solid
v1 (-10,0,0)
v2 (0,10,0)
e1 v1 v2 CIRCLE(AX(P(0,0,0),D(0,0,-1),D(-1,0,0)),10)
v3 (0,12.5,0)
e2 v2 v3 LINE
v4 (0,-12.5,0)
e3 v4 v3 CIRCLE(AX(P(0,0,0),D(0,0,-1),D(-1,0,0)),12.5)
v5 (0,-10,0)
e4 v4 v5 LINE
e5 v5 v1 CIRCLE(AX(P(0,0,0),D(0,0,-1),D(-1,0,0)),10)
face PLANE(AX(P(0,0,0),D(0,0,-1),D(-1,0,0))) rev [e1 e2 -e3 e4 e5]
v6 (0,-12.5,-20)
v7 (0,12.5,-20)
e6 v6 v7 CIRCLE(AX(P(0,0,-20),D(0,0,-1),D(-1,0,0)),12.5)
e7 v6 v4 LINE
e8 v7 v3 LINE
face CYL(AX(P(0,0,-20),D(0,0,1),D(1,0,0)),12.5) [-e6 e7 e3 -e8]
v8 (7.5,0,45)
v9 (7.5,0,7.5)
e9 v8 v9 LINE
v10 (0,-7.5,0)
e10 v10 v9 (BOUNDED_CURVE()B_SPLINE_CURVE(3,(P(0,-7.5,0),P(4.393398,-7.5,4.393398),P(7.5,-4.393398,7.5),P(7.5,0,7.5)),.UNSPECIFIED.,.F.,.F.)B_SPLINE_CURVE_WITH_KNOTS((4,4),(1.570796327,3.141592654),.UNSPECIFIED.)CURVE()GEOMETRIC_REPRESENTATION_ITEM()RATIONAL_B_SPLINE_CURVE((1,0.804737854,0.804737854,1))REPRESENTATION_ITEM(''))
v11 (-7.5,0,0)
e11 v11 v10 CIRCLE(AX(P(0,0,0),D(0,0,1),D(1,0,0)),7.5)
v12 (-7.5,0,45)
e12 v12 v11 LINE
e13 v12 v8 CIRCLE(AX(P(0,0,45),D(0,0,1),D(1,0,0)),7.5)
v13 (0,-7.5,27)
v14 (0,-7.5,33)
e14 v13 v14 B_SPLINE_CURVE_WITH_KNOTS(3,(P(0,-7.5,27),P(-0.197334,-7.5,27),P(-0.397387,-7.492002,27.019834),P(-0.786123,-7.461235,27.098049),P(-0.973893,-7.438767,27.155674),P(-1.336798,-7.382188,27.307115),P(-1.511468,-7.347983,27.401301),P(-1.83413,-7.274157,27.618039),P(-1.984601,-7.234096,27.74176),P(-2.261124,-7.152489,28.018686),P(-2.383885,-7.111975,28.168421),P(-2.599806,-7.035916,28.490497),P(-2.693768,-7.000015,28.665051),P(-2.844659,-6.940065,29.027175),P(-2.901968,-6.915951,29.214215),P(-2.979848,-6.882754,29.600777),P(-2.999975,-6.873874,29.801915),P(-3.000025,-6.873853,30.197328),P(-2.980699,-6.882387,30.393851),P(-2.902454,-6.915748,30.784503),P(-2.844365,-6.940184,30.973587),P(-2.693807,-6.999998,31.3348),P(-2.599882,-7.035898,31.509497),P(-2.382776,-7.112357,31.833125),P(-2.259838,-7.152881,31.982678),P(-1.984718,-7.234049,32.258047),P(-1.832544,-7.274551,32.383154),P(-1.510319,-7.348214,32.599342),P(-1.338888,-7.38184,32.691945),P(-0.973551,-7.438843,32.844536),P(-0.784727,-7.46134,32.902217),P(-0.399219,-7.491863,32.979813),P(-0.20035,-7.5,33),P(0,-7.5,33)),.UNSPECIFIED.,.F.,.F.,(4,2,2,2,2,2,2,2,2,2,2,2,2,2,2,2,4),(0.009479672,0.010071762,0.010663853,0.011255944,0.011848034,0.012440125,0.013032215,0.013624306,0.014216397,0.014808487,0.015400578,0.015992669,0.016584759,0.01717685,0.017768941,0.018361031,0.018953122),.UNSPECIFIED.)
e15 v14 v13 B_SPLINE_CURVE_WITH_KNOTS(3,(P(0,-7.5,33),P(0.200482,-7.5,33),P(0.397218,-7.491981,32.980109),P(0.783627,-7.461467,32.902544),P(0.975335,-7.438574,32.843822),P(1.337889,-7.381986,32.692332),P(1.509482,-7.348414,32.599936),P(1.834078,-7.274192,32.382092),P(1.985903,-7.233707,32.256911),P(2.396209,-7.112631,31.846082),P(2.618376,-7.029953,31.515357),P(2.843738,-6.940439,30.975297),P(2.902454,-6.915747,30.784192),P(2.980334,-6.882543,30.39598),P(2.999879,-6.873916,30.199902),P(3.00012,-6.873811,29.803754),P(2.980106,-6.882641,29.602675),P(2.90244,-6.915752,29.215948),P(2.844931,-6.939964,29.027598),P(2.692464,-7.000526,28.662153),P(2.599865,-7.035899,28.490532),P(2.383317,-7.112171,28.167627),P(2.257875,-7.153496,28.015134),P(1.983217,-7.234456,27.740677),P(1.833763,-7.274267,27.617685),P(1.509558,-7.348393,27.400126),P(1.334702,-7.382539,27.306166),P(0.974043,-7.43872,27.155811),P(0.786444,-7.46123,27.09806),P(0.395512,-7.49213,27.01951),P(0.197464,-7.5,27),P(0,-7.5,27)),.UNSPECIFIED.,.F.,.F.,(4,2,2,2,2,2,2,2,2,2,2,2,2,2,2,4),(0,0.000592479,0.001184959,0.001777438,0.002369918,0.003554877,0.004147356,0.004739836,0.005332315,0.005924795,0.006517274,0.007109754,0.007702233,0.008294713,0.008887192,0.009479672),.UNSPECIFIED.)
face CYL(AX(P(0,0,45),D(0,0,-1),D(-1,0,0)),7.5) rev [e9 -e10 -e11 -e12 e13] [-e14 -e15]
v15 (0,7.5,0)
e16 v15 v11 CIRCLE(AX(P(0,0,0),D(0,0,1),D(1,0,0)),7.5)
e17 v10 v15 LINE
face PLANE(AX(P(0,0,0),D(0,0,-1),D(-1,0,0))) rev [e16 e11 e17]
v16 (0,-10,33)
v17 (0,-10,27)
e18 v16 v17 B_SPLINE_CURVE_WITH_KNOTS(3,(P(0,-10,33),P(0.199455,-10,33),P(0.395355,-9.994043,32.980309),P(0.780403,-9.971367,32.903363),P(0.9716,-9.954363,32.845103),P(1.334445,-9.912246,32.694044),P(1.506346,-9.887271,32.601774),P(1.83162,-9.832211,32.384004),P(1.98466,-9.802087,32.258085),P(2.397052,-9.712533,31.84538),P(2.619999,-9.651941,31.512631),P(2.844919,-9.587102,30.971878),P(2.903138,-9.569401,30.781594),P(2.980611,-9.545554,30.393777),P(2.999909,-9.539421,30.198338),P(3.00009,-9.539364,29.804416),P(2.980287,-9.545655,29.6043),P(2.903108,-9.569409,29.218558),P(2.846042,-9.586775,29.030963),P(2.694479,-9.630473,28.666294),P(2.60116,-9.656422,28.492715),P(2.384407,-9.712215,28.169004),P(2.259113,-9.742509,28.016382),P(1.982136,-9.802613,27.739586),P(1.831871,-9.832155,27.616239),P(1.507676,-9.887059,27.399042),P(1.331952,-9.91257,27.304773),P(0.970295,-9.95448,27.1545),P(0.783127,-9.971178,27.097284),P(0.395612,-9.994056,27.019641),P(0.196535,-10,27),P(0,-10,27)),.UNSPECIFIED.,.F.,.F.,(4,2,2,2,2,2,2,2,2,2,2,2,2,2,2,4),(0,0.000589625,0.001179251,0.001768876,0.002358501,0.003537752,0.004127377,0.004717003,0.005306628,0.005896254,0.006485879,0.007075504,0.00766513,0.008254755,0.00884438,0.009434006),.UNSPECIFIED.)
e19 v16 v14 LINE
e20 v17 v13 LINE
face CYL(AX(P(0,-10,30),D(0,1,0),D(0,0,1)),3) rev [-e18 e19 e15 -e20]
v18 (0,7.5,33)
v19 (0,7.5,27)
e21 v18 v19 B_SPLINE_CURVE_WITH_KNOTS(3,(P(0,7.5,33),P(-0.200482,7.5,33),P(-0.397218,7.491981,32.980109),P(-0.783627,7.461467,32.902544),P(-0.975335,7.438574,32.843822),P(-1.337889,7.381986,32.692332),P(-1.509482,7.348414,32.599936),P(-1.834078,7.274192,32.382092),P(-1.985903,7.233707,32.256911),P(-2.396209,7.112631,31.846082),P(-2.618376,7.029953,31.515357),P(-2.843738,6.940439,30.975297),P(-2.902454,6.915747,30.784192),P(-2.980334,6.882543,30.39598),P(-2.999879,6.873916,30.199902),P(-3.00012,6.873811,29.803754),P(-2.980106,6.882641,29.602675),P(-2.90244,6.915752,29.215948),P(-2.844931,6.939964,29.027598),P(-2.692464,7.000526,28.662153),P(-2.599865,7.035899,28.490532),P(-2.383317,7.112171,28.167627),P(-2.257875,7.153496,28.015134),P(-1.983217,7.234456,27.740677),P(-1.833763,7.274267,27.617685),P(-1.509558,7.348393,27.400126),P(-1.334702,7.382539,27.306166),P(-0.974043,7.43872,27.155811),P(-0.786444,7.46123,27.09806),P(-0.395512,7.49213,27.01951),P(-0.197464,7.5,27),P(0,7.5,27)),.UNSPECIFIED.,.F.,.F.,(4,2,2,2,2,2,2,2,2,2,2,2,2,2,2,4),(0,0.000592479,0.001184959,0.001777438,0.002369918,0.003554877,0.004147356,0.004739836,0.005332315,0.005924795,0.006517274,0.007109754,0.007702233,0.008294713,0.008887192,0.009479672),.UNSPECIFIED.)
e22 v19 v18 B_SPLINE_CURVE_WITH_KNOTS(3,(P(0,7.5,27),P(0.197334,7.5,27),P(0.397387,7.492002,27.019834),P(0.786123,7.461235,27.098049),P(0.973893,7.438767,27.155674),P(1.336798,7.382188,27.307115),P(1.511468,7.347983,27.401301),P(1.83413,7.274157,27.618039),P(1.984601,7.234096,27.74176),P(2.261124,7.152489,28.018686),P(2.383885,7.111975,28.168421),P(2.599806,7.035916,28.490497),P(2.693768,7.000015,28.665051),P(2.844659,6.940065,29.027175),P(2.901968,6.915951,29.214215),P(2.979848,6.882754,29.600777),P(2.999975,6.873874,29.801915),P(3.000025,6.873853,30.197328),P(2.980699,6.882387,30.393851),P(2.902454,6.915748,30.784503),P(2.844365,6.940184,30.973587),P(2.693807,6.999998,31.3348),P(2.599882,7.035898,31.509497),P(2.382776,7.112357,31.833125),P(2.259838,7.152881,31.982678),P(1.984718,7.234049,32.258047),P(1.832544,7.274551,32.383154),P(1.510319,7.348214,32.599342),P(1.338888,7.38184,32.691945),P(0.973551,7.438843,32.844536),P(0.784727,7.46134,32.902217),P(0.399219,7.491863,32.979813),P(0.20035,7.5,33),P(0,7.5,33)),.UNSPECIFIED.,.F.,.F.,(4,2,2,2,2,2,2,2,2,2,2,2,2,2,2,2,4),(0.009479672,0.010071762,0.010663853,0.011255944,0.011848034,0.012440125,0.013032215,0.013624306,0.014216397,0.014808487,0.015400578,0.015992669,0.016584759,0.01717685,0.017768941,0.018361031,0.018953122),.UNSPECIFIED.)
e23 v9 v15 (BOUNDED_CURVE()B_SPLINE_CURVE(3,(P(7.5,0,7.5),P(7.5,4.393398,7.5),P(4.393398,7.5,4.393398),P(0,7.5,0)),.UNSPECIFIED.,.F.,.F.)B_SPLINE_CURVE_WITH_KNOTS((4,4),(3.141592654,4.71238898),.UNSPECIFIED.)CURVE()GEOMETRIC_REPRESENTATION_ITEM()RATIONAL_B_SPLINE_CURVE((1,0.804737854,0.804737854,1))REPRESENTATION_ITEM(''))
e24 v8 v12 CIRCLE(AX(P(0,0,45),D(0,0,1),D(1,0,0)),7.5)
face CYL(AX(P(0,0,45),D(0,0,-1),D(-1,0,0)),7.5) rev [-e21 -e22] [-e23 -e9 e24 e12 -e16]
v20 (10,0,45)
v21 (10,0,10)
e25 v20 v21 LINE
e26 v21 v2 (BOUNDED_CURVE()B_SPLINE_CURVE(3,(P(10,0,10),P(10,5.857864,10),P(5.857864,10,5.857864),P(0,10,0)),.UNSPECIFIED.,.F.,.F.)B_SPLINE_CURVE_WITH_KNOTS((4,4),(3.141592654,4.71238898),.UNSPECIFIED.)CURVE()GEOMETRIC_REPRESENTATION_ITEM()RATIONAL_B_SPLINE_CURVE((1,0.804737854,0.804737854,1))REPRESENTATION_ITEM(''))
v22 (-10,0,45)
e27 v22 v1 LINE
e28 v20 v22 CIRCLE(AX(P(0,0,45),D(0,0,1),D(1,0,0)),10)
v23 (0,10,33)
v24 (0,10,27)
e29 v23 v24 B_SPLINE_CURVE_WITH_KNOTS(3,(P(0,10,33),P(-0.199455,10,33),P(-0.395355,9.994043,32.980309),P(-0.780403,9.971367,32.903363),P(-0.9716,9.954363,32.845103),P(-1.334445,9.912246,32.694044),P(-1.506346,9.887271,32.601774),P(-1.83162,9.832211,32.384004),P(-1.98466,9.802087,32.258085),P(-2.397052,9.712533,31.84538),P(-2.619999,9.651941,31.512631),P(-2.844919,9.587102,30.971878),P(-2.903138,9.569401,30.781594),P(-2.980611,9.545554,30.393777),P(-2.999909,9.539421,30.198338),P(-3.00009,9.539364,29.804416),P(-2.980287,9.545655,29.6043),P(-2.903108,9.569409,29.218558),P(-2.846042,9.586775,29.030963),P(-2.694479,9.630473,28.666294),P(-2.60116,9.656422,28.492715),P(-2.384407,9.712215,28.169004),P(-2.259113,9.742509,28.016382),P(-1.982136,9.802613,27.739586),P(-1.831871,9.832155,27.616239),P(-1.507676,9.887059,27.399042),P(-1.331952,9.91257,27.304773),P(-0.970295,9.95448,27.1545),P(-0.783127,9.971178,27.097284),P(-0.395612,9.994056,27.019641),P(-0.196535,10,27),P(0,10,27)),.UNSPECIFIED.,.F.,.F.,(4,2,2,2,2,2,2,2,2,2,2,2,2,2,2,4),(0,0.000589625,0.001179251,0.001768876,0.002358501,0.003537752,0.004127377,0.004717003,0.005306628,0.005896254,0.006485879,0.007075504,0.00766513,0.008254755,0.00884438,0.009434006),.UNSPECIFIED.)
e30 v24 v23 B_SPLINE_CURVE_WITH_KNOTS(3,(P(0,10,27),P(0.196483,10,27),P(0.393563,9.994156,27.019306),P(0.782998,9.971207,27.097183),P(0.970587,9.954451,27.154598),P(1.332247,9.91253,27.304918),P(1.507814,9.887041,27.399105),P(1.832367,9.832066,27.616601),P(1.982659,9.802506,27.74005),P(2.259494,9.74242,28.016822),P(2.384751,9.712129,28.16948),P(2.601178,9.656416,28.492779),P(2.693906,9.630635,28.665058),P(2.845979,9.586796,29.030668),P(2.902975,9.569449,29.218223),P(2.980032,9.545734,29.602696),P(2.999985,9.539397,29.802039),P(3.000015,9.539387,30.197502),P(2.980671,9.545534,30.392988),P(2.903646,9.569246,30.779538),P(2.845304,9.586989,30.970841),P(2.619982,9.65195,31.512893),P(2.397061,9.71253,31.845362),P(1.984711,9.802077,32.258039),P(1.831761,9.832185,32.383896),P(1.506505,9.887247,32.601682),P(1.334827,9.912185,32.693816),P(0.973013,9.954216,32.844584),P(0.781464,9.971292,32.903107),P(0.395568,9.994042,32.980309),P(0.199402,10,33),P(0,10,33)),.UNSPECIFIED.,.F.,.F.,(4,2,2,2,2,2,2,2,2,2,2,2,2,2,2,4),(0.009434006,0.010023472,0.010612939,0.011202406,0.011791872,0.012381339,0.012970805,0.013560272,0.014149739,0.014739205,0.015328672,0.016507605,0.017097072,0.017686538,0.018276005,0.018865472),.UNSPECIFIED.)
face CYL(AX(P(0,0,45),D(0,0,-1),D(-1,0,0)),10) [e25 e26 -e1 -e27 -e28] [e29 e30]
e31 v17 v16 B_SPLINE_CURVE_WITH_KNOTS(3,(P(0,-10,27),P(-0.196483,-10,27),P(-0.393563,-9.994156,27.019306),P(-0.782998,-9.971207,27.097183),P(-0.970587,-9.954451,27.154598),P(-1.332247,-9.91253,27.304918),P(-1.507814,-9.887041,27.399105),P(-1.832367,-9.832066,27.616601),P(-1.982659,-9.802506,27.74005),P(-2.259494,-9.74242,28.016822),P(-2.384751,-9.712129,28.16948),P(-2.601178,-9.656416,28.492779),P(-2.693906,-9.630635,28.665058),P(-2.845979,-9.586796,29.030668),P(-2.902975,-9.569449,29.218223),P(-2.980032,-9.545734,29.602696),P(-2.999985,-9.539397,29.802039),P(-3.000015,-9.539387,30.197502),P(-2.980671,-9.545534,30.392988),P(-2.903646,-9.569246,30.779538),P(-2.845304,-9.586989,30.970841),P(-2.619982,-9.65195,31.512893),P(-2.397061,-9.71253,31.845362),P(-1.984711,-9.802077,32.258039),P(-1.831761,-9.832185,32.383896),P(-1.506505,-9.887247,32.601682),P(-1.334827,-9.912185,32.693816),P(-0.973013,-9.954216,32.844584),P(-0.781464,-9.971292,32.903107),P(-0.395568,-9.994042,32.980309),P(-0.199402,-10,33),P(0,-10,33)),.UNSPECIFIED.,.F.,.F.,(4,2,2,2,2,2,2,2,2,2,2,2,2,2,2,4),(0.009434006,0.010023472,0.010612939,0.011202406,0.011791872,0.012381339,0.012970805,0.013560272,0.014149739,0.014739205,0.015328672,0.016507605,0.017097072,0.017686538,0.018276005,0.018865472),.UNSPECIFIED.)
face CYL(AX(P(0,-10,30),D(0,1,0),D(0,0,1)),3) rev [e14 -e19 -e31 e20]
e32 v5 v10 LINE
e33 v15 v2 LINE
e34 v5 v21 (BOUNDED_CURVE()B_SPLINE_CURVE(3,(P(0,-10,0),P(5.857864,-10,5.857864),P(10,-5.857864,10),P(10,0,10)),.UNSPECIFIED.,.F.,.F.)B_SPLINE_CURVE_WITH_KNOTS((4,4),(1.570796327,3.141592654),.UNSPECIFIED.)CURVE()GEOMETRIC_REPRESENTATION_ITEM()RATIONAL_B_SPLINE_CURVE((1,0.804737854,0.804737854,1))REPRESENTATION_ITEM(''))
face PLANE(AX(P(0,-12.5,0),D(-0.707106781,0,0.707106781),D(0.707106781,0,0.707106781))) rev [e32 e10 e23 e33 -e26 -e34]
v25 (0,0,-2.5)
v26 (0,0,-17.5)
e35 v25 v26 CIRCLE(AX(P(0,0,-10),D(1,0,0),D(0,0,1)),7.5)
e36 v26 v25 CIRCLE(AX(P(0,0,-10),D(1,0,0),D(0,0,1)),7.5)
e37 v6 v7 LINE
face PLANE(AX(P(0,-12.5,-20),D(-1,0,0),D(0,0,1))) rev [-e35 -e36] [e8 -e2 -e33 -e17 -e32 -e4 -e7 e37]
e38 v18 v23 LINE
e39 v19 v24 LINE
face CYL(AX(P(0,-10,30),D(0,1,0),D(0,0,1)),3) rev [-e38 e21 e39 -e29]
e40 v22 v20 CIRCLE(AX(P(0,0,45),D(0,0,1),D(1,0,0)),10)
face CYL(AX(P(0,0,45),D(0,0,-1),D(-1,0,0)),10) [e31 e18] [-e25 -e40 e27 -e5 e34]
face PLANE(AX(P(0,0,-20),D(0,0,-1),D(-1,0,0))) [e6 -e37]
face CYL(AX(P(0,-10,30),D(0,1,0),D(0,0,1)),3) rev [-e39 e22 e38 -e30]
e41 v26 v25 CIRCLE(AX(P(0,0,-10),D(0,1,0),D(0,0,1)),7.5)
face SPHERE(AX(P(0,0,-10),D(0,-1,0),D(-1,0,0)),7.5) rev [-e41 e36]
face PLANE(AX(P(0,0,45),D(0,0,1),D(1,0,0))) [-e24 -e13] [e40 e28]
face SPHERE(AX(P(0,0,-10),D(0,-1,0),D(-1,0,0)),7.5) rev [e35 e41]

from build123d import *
from build123d.topology import SkipClean

# Parameters (mm, degrees)
SKETCH1_R               = 10
SKETCH1_R_2             = 7.5
BOSS_EXTRUDE1_DEPTH     = 45
CUT_EXTRUDE1_DEPTH      = 48.16990566
CUT_EXTRUDE1_DEPTH_BACK = 48.16990566
SKETCH2_R               = 3
SKETCH3_R               = 12.5
BOSS_EXTRUDE2_DEPTH     = 20
CUT_EXTRUDE2_DEPTH      = 49.347699108
CUT_EXTRUDE2_DEPTH_BACK = 49.347699108


with BuildPart() as part:
    # Sketch1 → Boss-Extrude1 (new body)
    with BuildSketch(Plane.XY):
        with Locations(Location((0, 0, 0), (0, 0, 180))):
            Circle(SKETCH1_R)
        with Locations(Location((0, 0, 0), (0, 0, 180))):
            Circle(SKETCH1_R_2, mode=Mode.SUBTRACT)
    extrude(amount=BOSS_EXTRUDE1_DEPTH)

    # Sketch2 → Cut-Extrude1 (cut, two sides: drawn at the far end of the back side and taken through both)
    with BuildSketch(Plane(origin=(0, 0, 0), x_dir=(1, 0, 0), z_dir=(0, 1, 0)).offset(-CUT_EXTRUDE1_DEPTH_BACK)):
        with Locations(Location((0, -30, 0), (0, 0, 270))):
            Circle(SKETCH2_R)
    extrude(amount=CUT_EXTRUDE1_DEPTH + CUT_EXTRUDE1_DEPTH_BACK, mode=Mode.SUBTRACT)

    # Sketch3 → Boss-Extrude2 (add)
    with BuildSketch(Plane(origin=(0, 0, 0), x_dir=(-1, 0, 0), z_dir=(0, 0, -1))):
        Circle(SKETCH3_R)
    extrude(amount=BOSS_EXTRUDE2_DEPTH)

    # Sketch4 → Cut-Extrude2 (cut, two sides: drawn at the far end of the back side and taken through both)
    with BuildSketch(Plane(origin=(0, 0, 0), x_dir=(1, 0, 0), z_dir=(0, 1, 0)).offset(-CUT_EXTRUDE2_DEPTH_BACK)):
        Polygon((0, 20), (12.5, 20), (12.5, 0), (10, -10), (0, 0), align=None)
    extrude(amount=CUT_EXTRUDE2_DEPTH + CUT_EXTRUDE2_DEPTH_BACK, mode=Mode.SUBTRACT)

    # Sketch5 → Cut-Revolve3 (revolve, cut)
    with SkipClean():  # the faces are left unmerged after this step: merging them gives an invalid solid
        with BuildSketch(Plane(origin=(0, 0, 0), x_dir=(1, 0, 0), z_dir=(0, 1, 0))):
            with BuildLine():
                Line((0, 17.5), (0, 2.5))
                ThreePointArc((0, 2.5), (-7.5, 10), (0, 17.5))
            make_face()
        revolve(axis=Axis((0, 0, 0), (0, 0, -1)), mode=Mode.SUBTRACT)


solid = part.part
